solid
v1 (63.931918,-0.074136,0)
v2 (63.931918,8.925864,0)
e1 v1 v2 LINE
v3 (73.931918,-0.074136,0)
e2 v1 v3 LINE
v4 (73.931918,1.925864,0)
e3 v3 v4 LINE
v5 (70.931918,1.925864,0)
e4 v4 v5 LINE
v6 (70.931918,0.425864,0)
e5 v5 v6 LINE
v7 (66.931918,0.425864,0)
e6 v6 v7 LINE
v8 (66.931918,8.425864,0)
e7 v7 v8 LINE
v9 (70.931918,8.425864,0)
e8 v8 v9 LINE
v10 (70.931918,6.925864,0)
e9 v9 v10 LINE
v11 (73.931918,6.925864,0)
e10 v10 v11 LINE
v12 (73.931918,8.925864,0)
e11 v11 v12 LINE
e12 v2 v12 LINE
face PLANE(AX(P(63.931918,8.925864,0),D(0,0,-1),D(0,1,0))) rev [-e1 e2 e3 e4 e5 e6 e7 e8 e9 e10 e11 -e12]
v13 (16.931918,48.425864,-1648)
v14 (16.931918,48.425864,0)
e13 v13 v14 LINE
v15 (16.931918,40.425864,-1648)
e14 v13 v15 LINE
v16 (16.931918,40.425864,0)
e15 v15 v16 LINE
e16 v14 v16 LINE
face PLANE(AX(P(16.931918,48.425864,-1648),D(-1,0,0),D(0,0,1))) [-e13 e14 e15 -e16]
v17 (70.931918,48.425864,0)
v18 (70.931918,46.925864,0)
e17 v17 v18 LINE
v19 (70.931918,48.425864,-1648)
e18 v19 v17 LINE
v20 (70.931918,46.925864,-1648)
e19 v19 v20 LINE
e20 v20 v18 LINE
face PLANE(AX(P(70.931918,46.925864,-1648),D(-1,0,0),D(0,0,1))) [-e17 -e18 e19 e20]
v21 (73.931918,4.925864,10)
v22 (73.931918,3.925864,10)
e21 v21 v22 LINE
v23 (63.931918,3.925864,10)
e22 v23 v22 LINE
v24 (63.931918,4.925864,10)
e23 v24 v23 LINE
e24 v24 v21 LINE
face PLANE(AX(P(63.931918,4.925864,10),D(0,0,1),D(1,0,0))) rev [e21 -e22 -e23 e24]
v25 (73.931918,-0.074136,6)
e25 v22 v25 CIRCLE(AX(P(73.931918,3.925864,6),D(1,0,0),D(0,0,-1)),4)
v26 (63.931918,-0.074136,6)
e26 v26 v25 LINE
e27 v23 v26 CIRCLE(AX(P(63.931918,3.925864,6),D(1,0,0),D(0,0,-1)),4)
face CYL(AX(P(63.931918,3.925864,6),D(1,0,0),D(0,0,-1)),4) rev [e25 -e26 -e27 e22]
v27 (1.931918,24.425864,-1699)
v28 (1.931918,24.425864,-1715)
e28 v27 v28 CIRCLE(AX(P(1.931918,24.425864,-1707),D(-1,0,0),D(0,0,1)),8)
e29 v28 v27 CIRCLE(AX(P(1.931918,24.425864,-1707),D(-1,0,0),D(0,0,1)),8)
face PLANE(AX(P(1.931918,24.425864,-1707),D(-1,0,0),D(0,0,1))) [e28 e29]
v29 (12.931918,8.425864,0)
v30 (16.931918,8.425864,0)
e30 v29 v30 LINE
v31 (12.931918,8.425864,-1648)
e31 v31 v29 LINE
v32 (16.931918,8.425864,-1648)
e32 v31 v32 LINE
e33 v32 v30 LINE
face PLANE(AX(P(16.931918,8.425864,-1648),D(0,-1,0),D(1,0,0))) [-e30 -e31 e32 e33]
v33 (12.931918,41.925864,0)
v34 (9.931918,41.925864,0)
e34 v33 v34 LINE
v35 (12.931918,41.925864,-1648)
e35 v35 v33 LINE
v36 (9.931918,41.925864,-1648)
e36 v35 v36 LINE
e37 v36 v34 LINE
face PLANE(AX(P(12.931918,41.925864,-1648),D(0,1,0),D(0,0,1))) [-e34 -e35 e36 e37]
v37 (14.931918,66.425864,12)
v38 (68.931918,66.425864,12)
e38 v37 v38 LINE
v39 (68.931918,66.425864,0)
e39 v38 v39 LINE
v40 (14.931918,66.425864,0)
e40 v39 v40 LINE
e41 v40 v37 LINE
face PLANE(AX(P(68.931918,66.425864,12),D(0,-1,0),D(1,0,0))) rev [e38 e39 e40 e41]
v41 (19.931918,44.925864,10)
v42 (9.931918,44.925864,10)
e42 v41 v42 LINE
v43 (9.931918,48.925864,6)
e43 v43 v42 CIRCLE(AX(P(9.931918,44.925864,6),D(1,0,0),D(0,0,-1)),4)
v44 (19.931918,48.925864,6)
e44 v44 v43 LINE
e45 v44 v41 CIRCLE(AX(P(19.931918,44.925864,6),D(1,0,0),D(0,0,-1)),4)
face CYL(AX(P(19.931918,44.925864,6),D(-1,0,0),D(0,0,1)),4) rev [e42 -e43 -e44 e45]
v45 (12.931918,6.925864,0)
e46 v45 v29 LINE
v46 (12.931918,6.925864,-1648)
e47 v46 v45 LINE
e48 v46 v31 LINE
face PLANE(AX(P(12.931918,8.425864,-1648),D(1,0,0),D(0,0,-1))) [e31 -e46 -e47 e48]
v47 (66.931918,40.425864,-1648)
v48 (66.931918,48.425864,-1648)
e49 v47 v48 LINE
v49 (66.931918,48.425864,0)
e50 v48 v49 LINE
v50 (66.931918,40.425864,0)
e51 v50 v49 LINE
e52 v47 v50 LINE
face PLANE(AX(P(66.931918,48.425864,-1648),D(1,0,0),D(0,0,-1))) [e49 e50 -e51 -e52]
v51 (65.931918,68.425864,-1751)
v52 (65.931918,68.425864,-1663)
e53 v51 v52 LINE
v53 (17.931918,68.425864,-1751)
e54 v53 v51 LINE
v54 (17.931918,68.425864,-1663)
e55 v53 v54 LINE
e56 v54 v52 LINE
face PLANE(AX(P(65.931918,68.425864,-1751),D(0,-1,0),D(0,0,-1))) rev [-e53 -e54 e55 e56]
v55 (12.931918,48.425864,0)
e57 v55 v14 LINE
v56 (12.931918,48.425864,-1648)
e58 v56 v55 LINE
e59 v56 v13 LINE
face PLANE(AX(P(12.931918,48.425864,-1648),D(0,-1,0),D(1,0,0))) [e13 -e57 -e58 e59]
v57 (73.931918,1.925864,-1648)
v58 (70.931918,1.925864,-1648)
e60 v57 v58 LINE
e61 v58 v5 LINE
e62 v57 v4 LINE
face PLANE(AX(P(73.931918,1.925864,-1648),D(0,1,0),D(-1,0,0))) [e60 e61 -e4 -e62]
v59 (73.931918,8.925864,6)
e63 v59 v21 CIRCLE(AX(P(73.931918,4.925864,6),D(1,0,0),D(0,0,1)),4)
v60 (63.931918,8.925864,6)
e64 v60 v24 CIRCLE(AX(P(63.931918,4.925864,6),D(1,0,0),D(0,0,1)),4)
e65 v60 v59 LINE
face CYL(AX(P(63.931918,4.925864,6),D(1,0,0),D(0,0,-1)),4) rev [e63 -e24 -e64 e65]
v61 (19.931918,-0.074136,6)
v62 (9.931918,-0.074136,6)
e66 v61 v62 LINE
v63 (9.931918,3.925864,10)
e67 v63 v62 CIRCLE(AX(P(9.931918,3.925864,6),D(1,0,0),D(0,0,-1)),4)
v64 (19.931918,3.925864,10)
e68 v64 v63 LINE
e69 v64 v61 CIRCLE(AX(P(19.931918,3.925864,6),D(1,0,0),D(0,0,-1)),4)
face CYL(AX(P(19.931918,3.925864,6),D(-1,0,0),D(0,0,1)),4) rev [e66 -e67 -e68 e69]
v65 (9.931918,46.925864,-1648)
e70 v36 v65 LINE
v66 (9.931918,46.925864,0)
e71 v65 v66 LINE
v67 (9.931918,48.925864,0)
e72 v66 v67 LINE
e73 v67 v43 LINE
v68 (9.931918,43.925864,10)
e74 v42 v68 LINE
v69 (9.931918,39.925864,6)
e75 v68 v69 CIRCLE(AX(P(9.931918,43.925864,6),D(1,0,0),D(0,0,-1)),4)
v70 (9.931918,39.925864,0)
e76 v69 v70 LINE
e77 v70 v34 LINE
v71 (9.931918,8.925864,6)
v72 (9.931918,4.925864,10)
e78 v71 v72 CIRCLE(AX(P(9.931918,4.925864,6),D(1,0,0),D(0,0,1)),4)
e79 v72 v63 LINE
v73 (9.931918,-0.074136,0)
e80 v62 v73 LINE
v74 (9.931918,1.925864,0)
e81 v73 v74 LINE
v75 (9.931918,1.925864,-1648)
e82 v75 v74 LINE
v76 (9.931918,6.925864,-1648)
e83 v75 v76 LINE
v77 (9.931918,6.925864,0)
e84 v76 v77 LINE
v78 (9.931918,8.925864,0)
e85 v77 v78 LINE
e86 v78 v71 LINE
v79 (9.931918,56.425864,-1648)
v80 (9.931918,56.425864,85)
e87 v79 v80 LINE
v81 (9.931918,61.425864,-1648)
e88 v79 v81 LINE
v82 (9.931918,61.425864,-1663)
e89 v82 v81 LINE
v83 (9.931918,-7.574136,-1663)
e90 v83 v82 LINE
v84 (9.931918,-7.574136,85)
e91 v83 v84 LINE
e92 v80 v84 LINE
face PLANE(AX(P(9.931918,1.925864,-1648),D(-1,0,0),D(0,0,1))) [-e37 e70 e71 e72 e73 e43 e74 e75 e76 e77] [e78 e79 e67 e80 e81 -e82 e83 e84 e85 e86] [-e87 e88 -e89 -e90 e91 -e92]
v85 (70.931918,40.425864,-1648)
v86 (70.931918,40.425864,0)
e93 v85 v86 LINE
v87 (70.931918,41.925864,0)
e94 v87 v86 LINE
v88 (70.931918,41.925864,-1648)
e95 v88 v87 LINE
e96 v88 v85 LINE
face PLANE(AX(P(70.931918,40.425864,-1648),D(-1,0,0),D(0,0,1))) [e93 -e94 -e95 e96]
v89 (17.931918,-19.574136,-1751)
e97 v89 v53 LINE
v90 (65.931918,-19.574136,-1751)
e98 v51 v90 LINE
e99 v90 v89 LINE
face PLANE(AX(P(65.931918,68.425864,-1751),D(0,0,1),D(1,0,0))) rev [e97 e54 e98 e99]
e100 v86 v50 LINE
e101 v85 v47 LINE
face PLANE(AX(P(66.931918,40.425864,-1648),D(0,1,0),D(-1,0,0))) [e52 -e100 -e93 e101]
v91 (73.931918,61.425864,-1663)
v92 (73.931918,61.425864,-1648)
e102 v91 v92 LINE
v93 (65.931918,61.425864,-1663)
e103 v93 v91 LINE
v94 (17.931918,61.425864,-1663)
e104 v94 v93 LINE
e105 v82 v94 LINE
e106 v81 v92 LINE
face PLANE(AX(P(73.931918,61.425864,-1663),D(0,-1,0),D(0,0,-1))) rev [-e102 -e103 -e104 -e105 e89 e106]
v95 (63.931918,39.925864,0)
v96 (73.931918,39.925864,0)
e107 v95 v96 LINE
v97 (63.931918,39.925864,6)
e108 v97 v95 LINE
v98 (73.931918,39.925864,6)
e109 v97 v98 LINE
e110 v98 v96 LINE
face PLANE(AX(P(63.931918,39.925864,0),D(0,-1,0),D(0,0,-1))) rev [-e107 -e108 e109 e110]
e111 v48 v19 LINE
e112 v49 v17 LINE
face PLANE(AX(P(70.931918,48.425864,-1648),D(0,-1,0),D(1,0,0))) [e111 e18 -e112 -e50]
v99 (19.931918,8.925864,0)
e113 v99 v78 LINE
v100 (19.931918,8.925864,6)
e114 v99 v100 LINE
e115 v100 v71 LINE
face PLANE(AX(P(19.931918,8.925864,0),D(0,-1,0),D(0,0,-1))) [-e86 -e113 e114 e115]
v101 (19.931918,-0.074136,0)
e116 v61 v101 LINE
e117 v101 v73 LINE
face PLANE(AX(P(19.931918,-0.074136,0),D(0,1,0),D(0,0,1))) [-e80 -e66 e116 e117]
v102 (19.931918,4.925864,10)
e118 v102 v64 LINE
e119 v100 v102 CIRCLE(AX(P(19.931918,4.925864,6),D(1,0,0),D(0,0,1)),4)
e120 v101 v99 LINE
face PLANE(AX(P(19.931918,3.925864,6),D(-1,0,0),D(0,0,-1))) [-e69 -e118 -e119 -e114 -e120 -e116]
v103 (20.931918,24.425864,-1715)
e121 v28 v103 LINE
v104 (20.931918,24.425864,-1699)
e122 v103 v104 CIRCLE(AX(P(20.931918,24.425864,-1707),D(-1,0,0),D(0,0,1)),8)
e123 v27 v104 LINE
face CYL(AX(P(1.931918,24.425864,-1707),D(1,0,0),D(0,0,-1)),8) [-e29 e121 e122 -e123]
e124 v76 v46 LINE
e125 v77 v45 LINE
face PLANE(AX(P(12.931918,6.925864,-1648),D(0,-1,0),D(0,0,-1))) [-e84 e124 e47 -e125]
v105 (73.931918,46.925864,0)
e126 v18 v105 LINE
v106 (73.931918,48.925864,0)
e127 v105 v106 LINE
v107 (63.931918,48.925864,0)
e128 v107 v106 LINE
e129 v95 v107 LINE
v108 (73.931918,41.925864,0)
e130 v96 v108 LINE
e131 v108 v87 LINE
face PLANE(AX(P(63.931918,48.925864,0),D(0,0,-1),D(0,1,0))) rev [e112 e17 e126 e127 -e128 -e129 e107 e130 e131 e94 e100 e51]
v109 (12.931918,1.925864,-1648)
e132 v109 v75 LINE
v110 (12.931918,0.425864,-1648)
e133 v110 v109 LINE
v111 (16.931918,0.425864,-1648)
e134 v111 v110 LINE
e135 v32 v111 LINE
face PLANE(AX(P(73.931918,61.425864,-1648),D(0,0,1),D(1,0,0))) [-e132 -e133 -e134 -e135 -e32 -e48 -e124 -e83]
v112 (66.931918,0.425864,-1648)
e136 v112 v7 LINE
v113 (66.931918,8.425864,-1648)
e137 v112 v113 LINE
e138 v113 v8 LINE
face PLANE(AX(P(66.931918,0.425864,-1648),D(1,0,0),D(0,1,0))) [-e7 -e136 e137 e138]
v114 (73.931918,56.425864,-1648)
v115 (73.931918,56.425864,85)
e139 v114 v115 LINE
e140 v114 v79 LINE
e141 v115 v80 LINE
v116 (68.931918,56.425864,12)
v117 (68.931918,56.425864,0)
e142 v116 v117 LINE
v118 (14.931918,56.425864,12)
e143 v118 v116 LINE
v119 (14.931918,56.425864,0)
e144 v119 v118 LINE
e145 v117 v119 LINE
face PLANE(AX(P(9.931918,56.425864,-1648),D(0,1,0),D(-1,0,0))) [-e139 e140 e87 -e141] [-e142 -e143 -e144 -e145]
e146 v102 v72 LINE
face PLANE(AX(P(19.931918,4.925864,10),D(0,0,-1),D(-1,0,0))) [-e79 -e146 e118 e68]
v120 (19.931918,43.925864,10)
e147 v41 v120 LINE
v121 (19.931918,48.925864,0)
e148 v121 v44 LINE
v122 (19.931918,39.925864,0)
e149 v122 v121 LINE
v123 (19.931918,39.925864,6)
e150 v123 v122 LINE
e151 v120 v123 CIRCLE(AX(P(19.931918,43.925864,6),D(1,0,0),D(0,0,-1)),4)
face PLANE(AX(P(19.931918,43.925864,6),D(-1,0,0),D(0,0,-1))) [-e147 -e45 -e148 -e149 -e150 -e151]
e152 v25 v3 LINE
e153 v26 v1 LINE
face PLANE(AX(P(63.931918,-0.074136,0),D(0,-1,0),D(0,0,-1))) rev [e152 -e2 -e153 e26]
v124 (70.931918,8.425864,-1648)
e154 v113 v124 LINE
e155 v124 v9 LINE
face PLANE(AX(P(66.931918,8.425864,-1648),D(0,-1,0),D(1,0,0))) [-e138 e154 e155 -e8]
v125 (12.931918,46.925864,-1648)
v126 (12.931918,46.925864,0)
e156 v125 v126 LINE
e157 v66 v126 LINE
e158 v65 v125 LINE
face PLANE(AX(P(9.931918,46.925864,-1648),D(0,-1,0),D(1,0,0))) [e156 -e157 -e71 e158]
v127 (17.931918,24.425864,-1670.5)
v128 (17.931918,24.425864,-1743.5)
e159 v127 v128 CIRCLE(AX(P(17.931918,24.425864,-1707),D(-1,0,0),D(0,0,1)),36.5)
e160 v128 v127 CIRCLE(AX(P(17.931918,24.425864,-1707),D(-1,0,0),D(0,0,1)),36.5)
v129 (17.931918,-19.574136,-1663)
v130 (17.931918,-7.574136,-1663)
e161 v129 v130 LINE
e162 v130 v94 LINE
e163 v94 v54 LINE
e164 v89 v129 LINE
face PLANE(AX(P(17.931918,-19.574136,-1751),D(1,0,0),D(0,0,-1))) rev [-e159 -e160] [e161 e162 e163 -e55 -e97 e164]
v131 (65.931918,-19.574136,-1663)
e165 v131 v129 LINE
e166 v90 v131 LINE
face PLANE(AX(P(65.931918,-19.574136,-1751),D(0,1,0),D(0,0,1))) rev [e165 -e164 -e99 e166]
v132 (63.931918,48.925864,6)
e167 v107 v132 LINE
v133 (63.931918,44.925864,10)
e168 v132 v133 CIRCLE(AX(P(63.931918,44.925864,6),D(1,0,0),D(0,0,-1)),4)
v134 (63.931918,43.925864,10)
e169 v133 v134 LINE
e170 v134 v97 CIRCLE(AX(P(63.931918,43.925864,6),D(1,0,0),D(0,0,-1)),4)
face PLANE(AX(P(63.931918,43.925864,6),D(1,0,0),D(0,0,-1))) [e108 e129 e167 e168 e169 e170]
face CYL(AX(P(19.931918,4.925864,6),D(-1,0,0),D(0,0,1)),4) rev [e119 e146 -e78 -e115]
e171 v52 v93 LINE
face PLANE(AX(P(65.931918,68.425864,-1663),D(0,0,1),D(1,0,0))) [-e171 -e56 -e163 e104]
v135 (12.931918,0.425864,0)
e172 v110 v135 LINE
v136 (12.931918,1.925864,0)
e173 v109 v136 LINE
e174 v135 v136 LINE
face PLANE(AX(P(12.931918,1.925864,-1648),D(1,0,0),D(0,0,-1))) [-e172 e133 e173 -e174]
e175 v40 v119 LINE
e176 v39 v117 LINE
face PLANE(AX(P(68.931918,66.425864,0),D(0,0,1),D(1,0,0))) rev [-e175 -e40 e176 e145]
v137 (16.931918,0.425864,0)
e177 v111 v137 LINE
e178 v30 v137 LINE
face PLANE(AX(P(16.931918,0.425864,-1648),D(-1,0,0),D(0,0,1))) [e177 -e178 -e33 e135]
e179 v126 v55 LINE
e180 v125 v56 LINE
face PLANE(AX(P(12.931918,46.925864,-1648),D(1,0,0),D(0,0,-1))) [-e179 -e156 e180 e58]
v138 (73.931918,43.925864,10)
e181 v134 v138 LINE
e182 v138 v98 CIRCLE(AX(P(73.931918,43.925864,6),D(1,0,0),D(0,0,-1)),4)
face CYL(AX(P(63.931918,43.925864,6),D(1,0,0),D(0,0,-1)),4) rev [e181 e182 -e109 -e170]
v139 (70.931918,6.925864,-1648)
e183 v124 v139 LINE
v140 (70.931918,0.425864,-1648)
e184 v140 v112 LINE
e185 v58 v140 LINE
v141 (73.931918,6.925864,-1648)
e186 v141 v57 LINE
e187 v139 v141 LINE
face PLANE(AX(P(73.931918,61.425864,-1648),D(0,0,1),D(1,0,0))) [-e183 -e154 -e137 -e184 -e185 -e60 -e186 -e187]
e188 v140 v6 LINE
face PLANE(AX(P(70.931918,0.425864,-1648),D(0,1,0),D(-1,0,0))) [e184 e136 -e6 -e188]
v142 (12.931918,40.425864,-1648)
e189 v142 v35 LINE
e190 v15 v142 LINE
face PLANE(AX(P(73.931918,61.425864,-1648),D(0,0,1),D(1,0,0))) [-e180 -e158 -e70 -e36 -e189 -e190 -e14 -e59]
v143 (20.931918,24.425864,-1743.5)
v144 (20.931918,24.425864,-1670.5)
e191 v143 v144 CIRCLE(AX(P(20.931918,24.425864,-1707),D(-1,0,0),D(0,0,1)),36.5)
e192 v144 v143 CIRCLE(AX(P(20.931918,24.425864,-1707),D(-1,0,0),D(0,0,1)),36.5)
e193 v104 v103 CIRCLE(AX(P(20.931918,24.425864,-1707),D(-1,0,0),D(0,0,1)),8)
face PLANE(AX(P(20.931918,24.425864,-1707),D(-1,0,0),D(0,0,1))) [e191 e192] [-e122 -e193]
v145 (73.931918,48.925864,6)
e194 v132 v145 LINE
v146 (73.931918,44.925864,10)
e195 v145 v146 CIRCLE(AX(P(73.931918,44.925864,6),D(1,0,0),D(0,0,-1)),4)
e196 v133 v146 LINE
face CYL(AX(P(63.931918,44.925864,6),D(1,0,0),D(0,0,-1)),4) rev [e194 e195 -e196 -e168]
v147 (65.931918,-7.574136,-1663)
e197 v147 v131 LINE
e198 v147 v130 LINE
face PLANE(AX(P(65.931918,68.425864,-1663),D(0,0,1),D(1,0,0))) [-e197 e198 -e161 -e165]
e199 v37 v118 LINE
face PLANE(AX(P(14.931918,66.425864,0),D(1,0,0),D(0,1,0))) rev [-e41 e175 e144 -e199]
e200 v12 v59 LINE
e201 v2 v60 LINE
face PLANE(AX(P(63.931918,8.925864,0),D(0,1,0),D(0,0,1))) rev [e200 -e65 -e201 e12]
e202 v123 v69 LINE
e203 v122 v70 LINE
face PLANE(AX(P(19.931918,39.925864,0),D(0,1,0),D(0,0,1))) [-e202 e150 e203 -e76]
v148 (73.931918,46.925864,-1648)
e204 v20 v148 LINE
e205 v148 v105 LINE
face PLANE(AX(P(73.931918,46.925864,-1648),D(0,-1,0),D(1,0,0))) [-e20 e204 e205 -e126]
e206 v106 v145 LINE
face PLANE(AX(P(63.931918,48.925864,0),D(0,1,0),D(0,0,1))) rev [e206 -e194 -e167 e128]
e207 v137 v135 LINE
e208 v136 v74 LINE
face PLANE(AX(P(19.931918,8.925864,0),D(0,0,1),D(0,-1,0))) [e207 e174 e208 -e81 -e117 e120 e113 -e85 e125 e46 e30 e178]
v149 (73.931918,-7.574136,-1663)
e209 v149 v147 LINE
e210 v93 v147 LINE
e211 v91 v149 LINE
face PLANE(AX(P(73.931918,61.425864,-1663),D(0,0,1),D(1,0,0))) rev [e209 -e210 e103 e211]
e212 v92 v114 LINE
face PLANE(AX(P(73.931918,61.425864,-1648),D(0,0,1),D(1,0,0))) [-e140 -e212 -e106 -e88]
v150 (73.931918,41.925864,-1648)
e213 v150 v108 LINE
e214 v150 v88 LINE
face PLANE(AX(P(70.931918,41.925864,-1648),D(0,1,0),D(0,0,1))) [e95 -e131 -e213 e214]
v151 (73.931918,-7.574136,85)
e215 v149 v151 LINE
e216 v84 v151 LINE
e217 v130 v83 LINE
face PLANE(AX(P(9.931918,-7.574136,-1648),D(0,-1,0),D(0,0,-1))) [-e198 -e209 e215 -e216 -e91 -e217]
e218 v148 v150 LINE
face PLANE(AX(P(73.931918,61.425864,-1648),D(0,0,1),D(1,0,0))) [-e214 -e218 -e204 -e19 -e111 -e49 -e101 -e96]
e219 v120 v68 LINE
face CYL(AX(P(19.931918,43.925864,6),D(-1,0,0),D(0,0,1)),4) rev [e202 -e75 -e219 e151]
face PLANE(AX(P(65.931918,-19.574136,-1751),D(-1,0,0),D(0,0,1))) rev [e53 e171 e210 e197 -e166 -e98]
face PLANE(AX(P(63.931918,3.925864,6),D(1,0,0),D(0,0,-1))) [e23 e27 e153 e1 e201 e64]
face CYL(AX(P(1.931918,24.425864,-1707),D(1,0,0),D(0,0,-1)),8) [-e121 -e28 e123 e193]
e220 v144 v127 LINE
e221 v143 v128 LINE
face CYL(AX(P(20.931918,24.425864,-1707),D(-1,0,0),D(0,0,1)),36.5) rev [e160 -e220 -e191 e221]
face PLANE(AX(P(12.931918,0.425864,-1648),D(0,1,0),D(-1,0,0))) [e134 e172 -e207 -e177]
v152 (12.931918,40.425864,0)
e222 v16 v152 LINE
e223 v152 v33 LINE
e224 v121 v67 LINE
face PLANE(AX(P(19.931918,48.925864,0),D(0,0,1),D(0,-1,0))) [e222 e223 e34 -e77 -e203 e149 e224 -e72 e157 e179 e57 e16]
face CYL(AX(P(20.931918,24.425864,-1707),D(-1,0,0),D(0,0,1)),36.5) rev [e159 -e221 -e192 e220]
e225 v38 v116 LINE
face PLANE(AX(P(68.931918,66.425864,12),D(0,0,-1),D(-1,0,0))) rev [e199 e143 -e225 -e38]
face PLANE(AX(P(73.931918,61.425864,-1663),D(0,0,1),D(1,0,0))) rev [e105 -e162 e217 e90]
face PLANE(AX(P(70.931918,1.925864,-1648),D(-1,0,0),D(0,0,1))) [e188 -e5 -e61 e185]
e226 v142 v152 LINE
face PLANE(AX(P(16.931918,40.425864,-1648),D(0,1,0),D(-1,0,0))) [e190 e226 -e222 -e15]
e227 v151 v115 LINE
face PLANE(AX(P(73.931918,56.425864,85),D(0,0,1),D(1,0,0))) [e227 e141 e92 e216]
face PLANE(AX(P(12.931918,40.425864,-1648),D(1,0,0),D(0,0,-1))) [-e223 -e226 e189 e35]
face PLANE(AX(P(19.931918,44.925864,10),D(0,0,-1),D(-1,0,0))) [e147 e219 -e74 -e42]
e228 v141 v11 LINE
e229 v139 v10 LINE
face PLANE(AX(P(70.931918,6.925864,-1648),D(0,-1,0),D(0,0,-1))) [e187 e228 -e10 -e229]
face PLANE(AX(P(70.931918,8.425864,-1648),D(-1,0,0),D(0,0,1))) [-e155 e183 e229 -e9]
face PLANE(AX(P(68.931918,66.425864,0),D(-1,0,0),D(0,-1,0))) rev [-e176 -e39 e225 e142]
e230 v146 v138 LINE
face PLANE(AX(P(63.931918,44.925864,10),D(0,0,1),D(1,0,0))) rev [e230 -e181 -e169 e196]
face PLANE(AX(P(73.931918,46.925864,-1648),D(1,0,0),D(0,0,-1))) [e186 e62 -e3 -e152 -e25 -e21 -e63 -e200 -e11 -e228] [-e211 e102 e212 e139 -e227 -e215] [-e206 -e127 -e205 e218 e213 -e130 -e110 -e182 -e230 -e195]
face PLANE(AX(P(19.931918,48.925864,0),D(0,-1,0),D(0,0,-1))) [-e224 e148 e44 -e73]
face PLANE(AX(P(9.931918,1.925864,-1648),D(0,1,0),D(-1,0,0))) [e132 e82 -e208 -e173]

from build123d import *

# Parameters (mm, degrees)
EXTRUDE_642_DEPTH   = 1648
SKETCH_2_W          = 64
SKETCH_2_H          = 64
EXTRUDE_1_DEPTH     = 85
SKETCH_4_W          = 54
SKETCH_4_H          = 12
EXTRUDE_2_DEPTH     = 10
CUT_EXTRUDE_1_DEPTH = 10
SKETCH_6_W          = 64
SKETCH_6_H          = 69
EXTRUDE_3_DEPTH     = 15
SKETCH_7_W          = 48
SKETCH_7_H          = 88
EXTRUDE_4_DEPTH     = 88
SKETCH_8_R          = 36.5
CUT_EXTRUDE_2_DEPTH = 3
SKETCH_9_R          = 8
EXTRUDE_5_DEPTH     = 19


with BuildPart() as part:
    # 草图1 → Extrude 642 (new body)
    with BuildSketch(Plane.XY):
        Polygon((9.931917842, 6.925864063), (9.931917842, 41.925864063), (12.931917842, 41.925864063), (12.931917842, 40.425864063), (16.931917842, 40.425864063), (16.931917842, 48.425864063), (12.931917842, 48.425864063), (12.931917842, 46.925864063), (9.931917842, 46.925864063), (9.931917842, 56.425864063), (73.931917842, 56.425864063), (73.931917842, 46.925864063), (70.931917842, 46.925864063), (70.931917842, 48.425864063), (66.931917842, 48.425864063), (66.931917842, 40.425864063), (70.931917842, 40.425864063), (70.931917842, 41.925864063), (73.931917842, 41.925864063), (73.931917842, 6.925864063), (70.931917842, 6.925864063), (70.931917842, 8.425864063), (66.931917842, 8.425864063), (66.931917842, 0.425864063), (70.931917842, 0.425864063), (70.931917842, 1.925864063), (73.931917842, 1.925864063), (73.931917842, -7.574135937), (9.931917842, -7.574135937), (9.931917842, 1.925864063), (12.931917842, 1.925864063), (12.931917842, 0.425864063), (16.931917842, 0.425864063), (16.931917842, 8.425864063), (12.931917842, 8.425864063), (12.931917842, 6.925864063), align=None)
    extrude(amount=-EXTRUDE_642_DEPTH)

    # 草图2 → 凸台-拉伸1 (add)
    with BuildSketch(Plane.XY):
        with Locations((41.931917842, 24.425864063)):
            Rectangle(SKETCH_2_W, SKETCH_2_H)
    extrude(amount=EXTRUDE_1_DEPTH)

    # 草图4 → 凸台-拉伸2 (add)
    with BuildSketch(Plane(origin=(0, 56.425864063, 0), x_dir=(-1, 0, 0), z_dir=(0, 1, 0))):
        with Locations((-41.931917842, 6)):
            Rectangle(SKETCH_4_W, SKETCH_4_H)
    extrude(amount=EXTRUDE_2_DEPTH)

    # 草图5 → 切除-拉伸1 (cut)
    with BuildSketch(Plane(origin=(73.931917842, 0, 0), x_dir=(0, 0, -1), z_dir=(1, 0, 0))):
        with BuildLine():
            Line((0, 48.925864063), (-6, 48.925864063))
            ThreePointArc((-6, 48.925864063), (-8.828427125, 47.754291188), (-10, 44.925864063))
            Line((-10, 44.925864063), (-10, 43.925864063))
            ThreePointArc((-10, 43.925864063), (-8.828427125, 41.097436938), (-6, 39.925864063))
            Line((-6, 39.925864063), (0, 39.925864063))
            Line((0, 39.925864063), (0, 48.925864063))
        make_face()
        with BuildLine():
            Line((0, 8.925864063), (-6, 8.925864063))
            ThreePointArc((-6, 8.925864063), (-8.828427125, 7.754291188), (-10, 4.925864063))
            Line((-10, 4.925864063), (-10, 3.925864063))
            ThreePointArc((-10, 3.925864063), (-8.828427125, 1.097436938), (-6, -0.074135937))
            Line((-6, -0.074135937), (0, -0.074135937))
            Line((0, -0.074135937), (0, 8.925864063))
        make_face()
    cut_extrude_1 = extrude(amount=-CUT_EXTRUDE_1_DEPTH, mode=Mode.SUBTRACT)

    # 镜向1: 切除-拉伸1 across plane
    add(cut_extrude_1.mirror(Plane.ZY.offset(-41.931917842)), mode=Mode.SUBTRACT)

    # 草图6 → 凸台-拉伸3 (add)
    with BuildSketch(Plane(origin=(0, 0, -1648), x_dir=(-1, 0, 0), z_dir=(0, 0, -1))):
        with Locations((-41.931917842, 26.925864063)):
            Rectangle(SKETCH_6_W, SKETCH_6_H)
    extrude(amount=EXTRUDE_3_DEPTH)

    # 草图7 → 凸台-拉伸4 (add)
    with BuildSketch(Plane(origin=(0, 0, -1663), x_dir=(-1, 0, 0), z_dir=(0, 0, -1))):
        with Locations((-41.931917842, 24.425864063)):
            Rectangle(SKETCH_7_W, SKETCH_7_H)
    extrude(amount=EXTRUDE_4_DEPTH)

    # 草图8 → 切除-拉伸2 (cut)
    with BuildSketch(Plane.ZY.offset(-17.931917842)):
        with Locations((-1707, 24.425864063)):
            Circle(SKETCH_8_R)
    extrude(amount=-CUT_EXTRUDE_2_DEPTH, mode=Mode.SUBTRACT)

    # 草图9 → 凸台-拉伸5 (add)
    with BuildSketch(Plane.ZY.offset(-20.931917842)):
        with Locations((-1707, 24.425864063)):
            Circle(SKETCH_9_R)
    extrude(amount=EXTRUDE_5_DEPTH)


solid = part.part
